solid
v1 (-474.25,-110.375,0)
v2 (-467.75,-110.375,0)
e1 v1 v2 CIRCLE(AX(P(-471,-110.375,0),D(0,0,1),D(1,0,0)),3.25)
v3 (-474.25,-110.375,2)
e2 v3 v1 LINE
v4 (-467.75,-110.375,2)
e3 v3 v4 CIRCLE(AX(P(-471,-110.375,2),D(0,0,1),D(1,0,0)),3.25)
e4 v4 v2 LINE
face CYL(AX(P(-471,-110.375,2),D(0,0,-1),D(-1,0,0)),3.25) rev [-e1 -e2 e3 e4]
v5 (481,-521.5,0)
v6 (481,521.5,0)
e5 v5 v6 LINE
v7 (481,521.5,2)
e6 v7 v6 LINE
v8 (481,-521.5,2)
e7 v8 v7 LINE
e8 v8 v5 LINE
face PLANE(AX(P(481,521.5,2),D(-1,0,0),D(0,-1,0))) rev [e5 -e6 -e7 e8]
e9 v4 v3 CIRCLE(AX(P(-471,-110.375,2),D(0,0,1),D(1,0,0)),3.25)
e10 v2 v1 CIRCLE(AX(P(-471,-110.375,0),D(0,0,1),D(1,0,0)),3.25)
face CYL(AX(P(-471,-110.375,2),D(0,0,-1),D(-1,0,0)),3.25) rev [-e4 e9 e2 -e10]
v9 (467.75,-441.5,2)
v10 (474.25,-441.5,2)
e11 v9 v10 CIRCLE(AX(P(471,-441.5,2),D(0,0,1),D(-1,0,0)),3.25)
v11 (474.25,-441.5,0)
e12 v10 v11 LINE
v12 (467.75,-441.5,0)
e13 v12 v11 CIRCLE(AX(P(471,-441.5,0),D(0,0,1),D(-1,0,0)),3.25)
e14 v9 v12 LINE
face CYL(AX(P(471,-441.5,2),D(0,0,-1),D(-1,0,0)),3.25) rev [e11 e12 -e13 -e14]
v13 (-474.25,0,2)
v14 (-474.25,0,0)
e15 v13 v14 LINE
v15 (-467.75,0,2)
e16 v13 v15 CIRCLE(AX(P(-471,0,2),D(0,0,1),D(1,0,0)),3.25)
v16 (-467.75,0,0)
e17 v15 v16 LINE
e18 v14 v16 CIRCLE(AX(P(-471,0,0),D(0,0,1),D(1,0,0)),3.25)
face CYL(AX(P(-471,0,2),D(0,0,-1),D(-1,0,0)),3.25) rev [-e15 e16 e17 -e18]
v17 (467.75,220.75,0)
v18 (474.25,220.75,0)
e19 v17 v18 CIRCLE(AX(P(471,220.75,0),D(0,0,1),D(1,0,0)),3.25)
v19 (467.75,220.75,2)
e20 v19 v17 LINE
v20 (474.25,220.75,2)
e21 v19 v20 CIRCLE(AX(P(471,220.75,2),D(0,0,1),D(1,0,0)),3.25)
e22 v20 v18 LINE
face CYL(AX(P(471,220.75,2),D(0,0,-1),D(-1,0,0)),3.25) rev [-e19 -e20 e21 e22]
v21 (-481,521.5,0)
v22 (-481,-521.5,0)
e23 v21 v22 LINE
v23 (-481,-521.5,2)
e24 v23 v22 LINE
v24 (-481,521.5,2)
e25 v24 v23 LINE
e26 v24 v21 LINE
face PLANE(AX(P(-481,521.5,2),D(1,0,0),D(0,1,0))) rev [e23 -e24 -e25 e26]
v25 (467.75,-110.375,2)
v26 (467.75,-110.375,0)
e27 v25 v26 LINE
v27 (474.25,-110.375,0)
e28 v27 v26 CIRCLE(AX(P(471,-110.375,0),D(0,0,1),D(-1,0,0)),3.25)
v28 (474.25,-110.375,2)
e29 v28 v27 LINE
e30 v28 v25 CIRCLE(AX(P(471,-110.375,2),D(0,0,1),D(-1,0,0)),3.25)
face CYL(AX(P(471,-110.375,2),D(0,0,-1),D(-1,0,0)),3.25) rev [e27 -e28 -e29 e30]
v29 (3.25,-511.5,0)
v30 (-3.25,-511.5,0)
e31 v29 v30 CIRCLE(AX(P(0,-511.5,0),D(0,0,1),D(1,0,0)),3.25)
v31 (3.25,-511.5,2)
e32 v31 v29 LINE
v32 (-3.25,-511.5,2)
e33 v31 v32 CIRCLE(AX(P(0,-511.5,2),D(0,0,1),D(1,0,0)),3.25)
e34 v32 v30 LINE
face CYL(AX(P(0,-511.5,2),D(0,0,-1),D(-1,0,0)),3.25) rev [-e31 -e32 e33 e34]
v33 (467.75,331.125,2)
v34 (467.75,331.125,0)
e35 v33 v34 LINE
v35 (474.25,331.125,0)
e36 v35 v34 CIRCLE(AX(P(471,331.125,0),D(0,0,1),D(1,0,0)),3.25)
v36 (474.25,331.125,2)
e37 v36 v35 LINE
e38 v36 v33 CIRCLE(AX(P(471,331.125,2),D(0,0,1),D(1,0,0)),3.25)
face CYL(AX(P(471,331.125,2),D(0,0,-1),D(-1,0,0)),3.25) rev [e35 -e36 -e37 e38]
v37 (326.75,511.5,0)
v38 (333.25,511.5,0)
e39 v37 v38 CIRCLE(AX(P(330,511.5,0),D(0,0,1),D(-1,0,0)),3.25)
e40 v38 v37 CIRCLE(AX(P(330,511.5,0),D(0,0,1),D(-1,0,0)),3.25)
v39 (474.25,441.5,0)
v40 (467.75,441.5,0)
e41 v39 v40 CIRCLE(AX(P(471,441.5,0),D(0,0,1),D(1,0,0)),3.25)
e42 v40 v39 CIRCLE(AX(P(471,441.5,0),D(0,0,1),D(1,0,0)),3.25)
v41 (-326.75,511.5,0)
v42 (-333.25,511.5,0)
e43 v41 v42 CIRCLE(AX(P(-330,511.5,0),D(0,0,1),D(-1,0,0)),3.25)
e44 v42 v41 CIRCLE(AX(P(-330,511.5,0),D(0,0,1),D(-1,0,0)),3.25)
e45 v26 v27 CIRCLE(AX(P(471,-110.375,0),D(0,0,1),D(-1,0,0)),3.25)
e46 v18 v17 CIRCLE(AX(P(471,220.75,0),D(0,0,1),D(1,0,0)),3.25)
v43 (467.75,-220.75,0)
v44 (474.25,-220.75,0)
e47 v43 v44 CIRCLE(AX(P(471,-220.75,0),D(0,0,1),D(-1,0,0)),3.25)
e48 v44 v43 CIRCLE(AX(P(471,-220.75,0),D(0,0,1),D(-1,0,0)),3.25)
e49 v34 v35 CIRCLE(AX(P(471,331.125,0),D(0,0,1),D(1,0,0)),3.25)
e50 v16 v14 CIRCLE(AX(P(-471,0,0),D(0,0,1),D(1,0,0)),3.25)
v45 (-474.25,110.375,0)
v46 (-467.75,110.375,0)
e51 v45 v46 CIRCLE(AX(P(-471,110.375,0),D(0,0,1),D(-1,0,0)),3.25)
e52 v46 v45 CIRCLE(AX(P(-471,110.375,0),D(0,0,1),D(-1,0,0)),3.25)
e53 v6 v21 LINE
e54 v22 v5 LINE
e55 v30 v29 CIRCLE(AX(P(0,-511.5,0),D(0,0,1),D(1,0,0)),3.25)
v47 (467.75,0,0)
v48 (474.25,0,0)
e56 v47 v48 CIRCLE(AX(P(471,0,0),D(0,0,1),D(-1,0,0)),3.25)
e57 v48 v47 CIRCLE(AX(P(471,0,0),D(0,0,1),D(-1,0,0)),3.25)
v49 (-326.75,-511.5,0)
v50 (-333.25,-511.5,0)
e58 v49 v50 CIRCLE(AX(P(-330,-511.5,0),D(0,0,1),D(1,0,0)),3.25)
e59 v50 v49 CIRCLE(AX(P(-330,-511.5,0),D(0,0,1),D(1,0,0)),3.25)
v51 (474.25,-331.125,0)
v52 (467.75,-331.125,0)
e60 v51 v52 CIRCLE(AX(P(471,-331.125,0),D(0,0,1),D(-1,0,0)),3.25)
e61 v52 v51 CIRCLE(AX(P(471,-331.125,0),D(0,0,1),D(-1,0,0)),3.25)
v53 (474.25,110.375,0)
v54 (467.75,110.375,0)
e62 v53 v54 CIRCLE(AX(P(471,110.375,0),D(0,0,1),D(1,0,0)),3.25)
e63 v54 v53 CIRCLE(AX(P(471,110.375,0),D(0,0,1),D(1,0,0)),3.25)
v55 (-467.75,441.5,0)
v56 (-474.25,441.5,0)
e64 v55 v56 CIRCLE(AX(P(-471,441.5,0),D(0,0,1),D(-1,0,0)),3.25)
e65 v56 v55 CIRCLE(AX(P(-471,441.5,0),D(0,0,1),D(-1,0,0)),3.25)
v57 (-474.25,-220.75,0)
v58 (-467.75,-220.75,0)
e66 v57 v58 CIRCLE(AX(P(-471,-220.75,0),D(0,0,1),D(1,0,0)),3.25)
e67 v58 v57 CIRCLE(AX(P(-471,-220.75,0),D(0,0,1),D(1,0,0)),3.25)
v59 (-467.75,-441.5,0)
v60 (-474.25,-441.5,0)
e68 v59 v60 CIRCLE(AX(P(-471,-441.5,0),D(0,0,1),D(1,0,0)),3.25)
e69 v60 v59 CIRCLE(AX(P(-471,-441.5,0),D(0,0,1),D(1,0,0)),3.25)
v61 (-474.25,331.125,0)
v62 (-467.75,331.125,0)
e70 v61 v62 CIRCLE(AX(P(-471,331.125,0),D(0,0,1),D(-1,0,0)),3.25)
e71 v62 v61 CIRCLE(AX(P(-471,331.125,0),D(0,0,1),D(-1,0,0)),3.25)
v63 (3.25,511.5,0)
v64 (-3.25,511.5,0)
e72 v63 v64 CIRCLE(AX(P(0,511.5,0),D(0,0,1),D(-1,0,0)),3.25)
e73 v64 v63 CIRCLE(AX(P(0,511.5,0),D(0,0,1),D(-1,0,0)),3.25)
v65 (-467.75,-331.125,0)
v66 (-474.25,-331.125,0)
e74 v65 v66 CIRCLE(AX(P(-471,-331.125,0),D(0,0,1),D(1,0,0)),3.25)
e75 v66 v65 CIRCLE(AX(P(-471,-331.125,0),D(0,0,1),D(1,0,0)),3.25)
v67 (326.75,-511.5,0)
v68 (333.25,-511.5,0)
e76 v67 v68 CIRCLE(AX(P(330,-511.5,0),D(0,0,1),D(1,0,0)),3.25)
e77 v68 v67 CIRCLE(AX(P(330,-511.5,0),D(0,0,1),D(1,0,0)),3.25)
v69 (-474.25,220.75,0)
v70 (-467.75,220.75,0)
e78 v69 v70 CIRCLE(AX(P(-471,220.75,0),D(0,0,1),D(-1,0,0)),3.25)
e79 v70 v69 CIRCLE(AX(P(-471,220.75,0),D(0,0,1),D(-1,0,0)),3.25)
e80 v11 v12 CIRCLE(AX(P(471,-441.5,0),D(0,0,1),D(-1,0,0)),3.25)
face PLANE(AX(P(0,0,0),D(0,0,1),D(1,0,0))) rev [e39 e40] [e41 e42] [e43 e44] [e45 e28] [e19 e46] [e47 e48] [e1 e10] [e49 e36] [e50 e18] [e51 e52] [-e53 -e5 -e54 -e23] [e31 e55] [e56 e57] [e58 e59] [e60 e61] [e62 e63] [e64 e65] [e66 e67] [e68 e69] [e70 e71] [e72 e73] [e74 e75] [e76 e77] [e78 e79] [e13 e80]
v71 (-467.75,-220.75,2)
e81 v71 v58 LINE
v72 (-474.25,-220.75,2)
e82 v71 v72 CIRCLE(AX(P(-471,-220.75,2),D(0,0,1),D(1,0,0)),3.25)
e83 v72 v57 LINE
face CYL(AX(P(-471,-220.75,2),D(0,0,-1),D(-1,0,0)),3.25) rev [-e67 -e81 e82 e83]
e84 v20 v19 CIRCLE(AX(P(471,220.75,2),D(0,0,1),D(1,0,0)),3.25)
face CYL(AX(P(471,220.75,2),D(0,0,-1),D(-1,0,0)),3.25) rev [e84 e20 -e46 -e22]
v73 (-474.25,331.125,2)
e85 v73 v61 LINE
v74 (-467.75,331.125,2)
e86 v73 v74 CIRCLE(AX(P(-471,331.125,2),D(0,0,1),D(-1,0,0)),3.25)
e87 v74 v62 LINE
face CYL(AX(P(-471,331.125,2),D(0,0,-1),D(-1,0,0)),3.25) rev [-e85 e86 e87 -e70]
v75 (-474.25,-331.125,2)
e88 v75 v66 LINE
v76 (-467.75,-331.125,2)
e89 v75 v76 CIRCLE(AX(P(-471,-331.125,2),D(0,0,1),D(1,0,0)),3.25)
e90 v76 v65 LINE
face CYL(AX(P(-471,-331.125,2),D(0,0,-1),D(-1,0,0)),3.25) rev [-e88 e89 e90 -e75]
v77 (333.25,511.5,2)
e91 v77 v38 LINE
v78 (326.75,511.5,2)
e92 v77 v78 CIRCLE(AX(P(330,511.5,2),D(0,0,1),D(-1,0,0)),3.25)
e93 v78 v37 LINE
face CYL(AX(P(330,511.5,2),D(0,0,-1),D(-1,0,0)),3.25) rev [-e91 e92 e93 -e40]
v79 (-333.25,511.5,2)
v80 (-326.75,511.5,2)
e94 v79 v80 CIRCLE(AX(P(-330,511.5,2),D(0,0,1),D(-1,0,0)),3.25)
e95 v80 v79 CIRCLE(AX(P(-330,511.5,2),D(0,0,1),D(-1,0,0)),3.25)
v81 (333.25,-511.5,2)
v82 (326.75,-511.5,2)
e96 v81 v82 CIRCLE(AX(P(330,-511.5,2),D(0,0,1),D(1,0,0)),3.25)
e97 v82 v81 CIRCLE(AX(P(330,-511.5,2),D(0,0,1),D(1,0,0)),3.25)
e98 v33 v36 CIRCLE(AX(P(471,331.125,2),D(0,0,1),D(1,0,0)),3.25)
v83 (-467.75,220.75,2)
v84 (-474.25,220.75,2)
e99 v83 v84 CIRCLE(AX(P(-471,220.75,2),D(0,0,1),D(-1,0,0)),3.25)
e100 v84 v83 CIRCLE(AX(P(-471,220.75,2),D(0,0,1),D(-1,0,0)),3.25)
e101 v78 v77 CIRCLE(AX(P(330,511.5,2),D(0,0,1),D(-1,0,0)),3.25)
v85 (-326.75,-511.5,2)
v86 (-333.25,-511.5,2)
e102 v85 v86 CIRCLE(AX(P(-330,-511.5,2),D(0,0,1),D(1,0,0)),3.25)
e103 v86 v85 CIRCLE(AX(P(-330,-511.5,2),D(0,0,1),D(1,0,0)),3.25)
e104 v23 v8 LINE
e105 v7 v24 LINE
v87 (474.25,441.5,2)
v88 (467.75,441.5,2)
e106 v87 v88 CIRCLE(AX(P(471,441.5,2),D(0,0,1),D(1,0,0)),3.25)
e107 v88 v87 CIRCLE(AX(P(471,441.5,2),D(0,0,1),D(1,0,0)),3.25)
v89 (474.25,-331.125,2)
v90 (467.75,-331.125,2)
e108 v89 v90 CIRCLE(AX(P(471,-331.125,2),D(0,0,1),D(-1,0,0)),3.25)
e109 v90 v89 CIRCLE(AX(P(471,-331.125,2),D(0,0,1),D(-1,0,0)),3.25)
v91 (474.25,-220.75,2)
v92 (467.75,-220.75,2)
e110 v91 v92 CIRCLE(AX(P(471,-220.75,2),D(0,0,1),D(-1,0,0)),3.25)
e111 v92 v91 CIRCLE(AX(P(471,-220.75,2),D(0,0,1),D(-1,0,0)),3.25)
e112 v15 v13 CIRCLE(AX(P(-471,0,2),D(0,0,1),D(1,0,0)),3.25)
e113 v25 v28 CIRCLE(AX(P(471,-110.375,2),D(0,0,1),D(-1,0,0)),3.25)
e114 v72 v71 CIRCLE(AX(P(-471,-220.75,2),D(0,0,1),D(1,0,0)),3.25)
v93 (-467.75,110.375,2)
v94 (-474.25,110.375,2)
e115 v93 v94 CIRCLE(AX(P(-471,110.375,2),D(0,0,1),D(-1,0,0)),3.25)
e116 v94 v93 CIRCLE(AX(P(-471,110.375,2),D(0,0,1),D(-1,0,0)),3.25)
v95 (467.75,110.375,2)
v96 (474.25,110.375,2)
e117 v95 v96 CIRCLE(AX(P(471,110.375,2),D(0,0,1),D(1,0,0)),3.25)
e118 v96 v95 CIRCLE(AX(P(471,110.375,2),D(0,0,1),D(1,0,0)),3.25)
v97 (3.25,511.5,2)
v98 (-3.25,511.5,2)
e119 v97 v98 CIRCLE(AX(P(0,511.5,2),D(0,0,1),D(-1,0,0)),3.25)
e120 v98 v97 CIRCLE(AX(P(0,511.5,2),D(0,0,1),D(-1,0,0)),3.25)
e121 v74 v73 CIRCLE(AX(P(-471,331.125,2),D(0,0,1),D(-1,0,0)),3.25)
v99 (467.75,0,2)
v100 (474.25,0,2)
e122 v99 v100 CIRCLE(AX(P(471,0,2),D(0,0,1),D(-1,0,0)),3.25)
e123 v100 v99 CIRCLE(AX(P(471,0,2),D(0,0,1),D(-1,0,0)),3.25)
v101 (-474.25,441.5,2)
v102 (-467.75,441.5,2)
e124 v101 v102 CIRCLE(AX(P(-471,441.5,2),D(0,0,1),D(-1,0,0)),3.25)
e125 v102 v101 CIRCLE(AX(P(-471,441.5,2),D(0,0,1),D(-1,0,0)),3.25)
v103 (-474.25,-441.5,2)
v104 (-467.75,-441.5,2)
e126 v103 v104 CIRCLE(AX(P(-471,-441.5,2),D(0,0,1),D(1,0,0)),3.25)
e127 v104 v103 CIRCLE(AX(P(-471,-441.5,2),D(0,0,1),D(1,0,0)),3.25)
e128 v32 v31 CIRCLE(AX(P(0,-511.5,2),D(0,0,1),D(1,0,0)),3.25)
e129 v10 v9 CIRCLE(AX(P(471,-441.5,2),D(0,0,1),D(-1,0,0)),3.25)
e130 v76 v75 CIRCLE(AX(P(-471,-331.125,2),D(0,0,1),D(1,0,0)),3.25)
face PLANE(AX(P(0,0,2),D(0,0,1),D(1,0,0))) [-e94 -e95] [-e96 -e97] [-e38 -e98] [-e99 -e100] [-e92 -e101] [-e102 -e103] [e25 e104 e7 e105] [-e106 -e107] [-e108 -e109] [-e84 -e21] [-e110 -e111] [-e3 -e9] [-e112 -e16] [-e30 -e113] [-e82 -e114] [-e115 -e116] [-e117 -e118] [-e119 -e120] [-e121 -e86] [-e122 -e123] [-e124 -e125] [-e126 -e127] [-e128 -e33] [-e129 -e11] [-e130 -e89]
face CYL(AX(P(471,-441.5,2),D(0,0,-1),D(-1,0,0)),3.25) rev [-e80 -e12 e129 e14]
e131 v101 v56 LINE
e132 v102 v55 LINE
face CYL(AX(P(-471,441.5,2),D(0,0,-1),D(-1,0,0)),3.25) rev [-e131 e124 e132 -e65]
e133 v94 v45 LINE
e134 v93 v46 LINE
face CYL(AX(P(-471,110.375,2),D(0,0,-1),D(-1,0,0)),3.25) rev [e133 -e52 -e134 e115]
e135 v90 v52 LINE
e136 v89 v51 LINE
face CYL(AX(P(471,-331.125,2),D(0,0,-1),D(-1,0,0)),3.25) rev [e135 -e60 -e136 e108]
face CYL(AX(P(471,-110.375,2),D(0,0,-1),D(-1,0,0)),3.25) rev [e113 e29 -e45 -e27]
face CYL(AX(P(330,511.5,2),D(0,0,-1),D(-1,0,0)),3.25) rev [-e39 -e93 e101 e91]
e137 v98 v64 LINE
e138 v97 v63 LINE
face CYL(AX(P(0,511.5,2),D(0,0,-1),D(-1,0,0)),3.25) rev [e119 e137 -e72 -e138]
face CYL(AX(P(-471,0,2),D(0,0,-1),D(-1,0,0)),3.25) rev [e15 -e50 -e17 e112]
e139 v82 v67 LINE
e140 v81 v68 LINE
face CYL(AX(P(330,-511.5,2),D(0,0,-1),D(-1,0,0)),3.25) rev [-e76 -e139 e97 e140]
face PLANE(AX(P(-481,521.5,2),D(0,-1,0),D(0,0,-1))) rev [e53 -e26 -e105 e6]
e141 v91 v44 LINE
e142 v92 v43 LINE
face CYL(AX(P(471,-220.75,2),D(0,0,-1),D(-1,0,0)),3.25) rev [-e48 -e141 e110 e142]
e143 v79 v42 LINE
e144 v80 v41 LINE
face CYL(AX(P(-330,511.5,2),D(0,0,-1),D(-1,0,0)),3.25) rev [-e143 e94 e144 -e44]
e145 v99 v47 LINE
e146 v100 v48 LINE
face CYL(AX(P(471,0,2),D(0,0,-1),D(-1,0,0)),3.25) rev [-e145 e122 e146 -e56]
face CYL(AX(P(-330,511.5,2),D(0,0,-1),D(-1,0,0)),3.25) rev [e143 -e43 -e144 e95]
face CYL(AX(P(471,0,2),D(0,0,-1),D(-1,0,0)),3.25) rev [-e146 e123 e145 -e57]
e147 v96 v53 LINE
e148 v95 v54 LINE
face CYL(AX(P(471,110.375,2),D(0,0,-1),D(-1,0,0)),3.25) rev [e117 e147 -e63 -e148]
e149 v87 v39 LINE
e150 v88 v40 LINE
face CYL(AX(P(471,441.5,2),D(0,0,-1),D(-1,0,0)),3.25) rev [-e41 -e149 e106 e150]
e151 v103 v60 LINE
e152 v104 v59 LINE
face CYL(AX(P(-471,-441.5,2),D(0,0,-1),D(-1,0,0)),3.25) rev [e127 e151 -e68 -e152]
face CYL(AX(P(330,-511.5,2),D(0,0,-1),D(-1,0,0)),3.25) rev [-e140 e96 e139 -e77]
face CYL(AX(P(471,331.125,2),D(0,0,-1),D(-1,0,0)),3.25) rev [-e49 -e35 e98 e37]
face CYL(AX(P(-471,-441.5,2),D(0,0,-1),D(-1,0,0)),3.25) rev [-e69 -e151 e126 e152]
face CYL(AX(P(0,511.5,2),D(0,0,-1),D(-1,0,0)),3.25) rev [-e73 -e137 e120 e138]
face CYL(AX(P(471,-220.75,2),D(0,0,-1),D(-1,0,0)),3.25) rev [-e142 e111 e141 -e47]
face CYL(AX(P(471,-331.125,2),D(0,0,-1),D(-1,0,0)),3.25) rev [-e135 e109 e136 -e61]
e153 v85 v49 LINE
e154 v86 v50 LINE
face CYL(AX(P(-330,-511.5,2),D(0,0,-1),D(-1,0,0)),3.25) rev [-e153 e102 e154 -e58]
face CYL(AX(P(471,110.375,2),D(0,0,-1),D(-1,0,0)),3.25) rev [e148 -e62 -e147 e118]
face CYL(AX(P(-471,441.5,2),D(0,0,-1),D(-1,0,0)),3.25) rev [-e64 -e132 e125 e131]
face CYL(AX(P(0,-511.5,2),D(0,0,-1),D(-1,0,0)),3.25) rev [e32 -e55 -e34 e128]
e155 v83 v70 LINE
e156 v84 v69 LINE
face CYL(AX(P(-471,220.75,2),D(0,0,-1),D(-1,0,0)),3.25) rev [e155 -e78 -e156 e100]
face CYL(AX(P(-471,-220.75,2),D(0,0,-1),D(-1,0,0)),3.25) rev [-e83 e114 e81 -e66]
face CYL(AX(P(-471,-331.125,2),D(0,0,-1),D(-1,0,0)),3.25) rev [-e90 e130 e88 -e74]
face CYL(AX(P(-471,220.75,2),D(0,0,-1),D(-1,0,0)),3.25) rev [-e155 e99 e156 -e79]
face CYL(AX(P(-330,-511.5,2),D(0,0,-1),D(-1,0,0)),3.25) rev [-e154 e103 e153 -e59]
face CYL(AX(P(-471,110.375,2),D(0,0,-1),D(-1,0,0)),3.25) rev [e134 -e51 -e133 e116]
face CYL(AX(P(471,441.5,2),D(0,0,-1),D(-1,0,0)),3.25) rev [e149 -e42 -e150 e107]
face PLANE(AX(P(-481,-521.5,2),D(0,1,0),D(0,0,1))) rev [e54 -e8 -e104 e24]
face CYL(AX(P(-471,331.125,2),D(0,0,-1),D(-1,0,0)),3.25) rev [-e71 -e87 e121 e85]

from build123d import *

# Parameters (mm, degrees)
SKETCH_1_W      = 962
SKETCH_1_H      = 1043
SKETCH_1_R      = 3.25
EXTRUDE_1_DEPTH = 2


with BuildPart() as part:
    # 草图1 → 凸台-拉伸1 (new body)
    with BuildSketch(Plane.XY):
        Rectangle(SKETCH_1_W, SKETCH_1_H)
        with Locations((-471, 0)):
            Circle(SKETCH_1_R, mode=Mode.SUBTRACT)
        with Locations((-471, -110.375)):
            Circle(SKETCH_1_R, mode=Mode.SUBTRACT)
        with Locations((-471, -220.75)):
            Circle(SKETCH_1_R, mode=Mode.SUBTRACT)
        with Locations((-471, -331.125)):
            Circle(SKETCH_1_R, mode=Mode.SUBTRACT)
        with Locations((-471, -441.5)):
            Circle(SKETCH_1_R, mode=Mode.SUBTRACT)
        with Locations((0, -511.5)):
            Circle(SKETCH_1_R, mode=Mode.SUBTRACT)
        with Locations(Location((0, 511.5, 0), (0, 0, 180))):
            Circle(SKETCH_1_R, mode=Mode.SUBTRACT)
        with Locations(Location((-471, 441.5, 0), (0, 0, 180))):
            Circle(SKETCH_1_R, mode=Mode.SUBTRACT)
        with Locations(Location((-471, 331.125, 0), (0, 0, 180))):
            Circle(SKETCH_1_R, mode=Mode.SUBTRACT)
        with Locations(Location((-471, 220.75, 0), (0, 0, 180))):
            Circle(SKETCH_1_R, mode=Mode.SUBTRACT)
        with Locations(Location((-471, 110.375, 0), (0, 0, 180))):
            Circle(SKETCH_1_R, mode=Mode.SUBTRACT)
        with Locations((471, 110.375)):
            Circle(SKETCH_1_R, mode=Mode.SUBTRACT)
        with Locations((471, 220.75)):
            Circle(SKETCH_1_R, mode=Mode.SUBTRACT)
        with Locations((471, 331.125)):
            Circle(SKETCH_1_R, mode=Mode.SUBTRACT)
        with Locations((471, 441.5)):
            Circle(SKETCH_1_R, mode=Mode.SUBTRACT)
        with Locations(Location((471, -441.5, 0), (0, 0, 180))):
            Circle(SKETCH_1_R, mode=Mode.SUBTRACT)
        with Locations(Location((471, -331.125, 0), (0, 0, 180))):
            Circle(SKETCH_1_R, mode=Mode.SUBTRACT)
        with Locations(Location((471, -220.75, 0), (0, 0, 180))):
            Circle(SKETCH_1_R, mode=Mode.SUBTRACT)
        with Locations(Location((471, -110.375, 0), (0, 0, 180))):
            Circle(SKETCH_1_R, mode=Mode.SUBTRACT)
        with Locations(Location((471, 0, 0), (0, 0, 180))):
            Circle(SKETCH_1_R, mode=Mode.SUBTRACT)
        with Locations((330, -511.5)):
            Circle(SKETCH_1_R, mode=Mode.SUBTRACT)
        with Locations((-330, -511.5)):
            Circle(SKETCH_1_R, mode=Mode.SUBTRACT)
        with Locations(Location((-330, 511.5, 0), (0, 0, 180))):
            Circle(SKETCH_1_R, mode=Mode.SUBTRACT)
        with Locations(Location((330, 511.5, 0), (0, 0, 180))):
            Circle(SKETCH_1_R, mode=Mode.SUBTRACT)
    extrude(amount=EXTRUDE_1_DEPTH)


solid = part.part
